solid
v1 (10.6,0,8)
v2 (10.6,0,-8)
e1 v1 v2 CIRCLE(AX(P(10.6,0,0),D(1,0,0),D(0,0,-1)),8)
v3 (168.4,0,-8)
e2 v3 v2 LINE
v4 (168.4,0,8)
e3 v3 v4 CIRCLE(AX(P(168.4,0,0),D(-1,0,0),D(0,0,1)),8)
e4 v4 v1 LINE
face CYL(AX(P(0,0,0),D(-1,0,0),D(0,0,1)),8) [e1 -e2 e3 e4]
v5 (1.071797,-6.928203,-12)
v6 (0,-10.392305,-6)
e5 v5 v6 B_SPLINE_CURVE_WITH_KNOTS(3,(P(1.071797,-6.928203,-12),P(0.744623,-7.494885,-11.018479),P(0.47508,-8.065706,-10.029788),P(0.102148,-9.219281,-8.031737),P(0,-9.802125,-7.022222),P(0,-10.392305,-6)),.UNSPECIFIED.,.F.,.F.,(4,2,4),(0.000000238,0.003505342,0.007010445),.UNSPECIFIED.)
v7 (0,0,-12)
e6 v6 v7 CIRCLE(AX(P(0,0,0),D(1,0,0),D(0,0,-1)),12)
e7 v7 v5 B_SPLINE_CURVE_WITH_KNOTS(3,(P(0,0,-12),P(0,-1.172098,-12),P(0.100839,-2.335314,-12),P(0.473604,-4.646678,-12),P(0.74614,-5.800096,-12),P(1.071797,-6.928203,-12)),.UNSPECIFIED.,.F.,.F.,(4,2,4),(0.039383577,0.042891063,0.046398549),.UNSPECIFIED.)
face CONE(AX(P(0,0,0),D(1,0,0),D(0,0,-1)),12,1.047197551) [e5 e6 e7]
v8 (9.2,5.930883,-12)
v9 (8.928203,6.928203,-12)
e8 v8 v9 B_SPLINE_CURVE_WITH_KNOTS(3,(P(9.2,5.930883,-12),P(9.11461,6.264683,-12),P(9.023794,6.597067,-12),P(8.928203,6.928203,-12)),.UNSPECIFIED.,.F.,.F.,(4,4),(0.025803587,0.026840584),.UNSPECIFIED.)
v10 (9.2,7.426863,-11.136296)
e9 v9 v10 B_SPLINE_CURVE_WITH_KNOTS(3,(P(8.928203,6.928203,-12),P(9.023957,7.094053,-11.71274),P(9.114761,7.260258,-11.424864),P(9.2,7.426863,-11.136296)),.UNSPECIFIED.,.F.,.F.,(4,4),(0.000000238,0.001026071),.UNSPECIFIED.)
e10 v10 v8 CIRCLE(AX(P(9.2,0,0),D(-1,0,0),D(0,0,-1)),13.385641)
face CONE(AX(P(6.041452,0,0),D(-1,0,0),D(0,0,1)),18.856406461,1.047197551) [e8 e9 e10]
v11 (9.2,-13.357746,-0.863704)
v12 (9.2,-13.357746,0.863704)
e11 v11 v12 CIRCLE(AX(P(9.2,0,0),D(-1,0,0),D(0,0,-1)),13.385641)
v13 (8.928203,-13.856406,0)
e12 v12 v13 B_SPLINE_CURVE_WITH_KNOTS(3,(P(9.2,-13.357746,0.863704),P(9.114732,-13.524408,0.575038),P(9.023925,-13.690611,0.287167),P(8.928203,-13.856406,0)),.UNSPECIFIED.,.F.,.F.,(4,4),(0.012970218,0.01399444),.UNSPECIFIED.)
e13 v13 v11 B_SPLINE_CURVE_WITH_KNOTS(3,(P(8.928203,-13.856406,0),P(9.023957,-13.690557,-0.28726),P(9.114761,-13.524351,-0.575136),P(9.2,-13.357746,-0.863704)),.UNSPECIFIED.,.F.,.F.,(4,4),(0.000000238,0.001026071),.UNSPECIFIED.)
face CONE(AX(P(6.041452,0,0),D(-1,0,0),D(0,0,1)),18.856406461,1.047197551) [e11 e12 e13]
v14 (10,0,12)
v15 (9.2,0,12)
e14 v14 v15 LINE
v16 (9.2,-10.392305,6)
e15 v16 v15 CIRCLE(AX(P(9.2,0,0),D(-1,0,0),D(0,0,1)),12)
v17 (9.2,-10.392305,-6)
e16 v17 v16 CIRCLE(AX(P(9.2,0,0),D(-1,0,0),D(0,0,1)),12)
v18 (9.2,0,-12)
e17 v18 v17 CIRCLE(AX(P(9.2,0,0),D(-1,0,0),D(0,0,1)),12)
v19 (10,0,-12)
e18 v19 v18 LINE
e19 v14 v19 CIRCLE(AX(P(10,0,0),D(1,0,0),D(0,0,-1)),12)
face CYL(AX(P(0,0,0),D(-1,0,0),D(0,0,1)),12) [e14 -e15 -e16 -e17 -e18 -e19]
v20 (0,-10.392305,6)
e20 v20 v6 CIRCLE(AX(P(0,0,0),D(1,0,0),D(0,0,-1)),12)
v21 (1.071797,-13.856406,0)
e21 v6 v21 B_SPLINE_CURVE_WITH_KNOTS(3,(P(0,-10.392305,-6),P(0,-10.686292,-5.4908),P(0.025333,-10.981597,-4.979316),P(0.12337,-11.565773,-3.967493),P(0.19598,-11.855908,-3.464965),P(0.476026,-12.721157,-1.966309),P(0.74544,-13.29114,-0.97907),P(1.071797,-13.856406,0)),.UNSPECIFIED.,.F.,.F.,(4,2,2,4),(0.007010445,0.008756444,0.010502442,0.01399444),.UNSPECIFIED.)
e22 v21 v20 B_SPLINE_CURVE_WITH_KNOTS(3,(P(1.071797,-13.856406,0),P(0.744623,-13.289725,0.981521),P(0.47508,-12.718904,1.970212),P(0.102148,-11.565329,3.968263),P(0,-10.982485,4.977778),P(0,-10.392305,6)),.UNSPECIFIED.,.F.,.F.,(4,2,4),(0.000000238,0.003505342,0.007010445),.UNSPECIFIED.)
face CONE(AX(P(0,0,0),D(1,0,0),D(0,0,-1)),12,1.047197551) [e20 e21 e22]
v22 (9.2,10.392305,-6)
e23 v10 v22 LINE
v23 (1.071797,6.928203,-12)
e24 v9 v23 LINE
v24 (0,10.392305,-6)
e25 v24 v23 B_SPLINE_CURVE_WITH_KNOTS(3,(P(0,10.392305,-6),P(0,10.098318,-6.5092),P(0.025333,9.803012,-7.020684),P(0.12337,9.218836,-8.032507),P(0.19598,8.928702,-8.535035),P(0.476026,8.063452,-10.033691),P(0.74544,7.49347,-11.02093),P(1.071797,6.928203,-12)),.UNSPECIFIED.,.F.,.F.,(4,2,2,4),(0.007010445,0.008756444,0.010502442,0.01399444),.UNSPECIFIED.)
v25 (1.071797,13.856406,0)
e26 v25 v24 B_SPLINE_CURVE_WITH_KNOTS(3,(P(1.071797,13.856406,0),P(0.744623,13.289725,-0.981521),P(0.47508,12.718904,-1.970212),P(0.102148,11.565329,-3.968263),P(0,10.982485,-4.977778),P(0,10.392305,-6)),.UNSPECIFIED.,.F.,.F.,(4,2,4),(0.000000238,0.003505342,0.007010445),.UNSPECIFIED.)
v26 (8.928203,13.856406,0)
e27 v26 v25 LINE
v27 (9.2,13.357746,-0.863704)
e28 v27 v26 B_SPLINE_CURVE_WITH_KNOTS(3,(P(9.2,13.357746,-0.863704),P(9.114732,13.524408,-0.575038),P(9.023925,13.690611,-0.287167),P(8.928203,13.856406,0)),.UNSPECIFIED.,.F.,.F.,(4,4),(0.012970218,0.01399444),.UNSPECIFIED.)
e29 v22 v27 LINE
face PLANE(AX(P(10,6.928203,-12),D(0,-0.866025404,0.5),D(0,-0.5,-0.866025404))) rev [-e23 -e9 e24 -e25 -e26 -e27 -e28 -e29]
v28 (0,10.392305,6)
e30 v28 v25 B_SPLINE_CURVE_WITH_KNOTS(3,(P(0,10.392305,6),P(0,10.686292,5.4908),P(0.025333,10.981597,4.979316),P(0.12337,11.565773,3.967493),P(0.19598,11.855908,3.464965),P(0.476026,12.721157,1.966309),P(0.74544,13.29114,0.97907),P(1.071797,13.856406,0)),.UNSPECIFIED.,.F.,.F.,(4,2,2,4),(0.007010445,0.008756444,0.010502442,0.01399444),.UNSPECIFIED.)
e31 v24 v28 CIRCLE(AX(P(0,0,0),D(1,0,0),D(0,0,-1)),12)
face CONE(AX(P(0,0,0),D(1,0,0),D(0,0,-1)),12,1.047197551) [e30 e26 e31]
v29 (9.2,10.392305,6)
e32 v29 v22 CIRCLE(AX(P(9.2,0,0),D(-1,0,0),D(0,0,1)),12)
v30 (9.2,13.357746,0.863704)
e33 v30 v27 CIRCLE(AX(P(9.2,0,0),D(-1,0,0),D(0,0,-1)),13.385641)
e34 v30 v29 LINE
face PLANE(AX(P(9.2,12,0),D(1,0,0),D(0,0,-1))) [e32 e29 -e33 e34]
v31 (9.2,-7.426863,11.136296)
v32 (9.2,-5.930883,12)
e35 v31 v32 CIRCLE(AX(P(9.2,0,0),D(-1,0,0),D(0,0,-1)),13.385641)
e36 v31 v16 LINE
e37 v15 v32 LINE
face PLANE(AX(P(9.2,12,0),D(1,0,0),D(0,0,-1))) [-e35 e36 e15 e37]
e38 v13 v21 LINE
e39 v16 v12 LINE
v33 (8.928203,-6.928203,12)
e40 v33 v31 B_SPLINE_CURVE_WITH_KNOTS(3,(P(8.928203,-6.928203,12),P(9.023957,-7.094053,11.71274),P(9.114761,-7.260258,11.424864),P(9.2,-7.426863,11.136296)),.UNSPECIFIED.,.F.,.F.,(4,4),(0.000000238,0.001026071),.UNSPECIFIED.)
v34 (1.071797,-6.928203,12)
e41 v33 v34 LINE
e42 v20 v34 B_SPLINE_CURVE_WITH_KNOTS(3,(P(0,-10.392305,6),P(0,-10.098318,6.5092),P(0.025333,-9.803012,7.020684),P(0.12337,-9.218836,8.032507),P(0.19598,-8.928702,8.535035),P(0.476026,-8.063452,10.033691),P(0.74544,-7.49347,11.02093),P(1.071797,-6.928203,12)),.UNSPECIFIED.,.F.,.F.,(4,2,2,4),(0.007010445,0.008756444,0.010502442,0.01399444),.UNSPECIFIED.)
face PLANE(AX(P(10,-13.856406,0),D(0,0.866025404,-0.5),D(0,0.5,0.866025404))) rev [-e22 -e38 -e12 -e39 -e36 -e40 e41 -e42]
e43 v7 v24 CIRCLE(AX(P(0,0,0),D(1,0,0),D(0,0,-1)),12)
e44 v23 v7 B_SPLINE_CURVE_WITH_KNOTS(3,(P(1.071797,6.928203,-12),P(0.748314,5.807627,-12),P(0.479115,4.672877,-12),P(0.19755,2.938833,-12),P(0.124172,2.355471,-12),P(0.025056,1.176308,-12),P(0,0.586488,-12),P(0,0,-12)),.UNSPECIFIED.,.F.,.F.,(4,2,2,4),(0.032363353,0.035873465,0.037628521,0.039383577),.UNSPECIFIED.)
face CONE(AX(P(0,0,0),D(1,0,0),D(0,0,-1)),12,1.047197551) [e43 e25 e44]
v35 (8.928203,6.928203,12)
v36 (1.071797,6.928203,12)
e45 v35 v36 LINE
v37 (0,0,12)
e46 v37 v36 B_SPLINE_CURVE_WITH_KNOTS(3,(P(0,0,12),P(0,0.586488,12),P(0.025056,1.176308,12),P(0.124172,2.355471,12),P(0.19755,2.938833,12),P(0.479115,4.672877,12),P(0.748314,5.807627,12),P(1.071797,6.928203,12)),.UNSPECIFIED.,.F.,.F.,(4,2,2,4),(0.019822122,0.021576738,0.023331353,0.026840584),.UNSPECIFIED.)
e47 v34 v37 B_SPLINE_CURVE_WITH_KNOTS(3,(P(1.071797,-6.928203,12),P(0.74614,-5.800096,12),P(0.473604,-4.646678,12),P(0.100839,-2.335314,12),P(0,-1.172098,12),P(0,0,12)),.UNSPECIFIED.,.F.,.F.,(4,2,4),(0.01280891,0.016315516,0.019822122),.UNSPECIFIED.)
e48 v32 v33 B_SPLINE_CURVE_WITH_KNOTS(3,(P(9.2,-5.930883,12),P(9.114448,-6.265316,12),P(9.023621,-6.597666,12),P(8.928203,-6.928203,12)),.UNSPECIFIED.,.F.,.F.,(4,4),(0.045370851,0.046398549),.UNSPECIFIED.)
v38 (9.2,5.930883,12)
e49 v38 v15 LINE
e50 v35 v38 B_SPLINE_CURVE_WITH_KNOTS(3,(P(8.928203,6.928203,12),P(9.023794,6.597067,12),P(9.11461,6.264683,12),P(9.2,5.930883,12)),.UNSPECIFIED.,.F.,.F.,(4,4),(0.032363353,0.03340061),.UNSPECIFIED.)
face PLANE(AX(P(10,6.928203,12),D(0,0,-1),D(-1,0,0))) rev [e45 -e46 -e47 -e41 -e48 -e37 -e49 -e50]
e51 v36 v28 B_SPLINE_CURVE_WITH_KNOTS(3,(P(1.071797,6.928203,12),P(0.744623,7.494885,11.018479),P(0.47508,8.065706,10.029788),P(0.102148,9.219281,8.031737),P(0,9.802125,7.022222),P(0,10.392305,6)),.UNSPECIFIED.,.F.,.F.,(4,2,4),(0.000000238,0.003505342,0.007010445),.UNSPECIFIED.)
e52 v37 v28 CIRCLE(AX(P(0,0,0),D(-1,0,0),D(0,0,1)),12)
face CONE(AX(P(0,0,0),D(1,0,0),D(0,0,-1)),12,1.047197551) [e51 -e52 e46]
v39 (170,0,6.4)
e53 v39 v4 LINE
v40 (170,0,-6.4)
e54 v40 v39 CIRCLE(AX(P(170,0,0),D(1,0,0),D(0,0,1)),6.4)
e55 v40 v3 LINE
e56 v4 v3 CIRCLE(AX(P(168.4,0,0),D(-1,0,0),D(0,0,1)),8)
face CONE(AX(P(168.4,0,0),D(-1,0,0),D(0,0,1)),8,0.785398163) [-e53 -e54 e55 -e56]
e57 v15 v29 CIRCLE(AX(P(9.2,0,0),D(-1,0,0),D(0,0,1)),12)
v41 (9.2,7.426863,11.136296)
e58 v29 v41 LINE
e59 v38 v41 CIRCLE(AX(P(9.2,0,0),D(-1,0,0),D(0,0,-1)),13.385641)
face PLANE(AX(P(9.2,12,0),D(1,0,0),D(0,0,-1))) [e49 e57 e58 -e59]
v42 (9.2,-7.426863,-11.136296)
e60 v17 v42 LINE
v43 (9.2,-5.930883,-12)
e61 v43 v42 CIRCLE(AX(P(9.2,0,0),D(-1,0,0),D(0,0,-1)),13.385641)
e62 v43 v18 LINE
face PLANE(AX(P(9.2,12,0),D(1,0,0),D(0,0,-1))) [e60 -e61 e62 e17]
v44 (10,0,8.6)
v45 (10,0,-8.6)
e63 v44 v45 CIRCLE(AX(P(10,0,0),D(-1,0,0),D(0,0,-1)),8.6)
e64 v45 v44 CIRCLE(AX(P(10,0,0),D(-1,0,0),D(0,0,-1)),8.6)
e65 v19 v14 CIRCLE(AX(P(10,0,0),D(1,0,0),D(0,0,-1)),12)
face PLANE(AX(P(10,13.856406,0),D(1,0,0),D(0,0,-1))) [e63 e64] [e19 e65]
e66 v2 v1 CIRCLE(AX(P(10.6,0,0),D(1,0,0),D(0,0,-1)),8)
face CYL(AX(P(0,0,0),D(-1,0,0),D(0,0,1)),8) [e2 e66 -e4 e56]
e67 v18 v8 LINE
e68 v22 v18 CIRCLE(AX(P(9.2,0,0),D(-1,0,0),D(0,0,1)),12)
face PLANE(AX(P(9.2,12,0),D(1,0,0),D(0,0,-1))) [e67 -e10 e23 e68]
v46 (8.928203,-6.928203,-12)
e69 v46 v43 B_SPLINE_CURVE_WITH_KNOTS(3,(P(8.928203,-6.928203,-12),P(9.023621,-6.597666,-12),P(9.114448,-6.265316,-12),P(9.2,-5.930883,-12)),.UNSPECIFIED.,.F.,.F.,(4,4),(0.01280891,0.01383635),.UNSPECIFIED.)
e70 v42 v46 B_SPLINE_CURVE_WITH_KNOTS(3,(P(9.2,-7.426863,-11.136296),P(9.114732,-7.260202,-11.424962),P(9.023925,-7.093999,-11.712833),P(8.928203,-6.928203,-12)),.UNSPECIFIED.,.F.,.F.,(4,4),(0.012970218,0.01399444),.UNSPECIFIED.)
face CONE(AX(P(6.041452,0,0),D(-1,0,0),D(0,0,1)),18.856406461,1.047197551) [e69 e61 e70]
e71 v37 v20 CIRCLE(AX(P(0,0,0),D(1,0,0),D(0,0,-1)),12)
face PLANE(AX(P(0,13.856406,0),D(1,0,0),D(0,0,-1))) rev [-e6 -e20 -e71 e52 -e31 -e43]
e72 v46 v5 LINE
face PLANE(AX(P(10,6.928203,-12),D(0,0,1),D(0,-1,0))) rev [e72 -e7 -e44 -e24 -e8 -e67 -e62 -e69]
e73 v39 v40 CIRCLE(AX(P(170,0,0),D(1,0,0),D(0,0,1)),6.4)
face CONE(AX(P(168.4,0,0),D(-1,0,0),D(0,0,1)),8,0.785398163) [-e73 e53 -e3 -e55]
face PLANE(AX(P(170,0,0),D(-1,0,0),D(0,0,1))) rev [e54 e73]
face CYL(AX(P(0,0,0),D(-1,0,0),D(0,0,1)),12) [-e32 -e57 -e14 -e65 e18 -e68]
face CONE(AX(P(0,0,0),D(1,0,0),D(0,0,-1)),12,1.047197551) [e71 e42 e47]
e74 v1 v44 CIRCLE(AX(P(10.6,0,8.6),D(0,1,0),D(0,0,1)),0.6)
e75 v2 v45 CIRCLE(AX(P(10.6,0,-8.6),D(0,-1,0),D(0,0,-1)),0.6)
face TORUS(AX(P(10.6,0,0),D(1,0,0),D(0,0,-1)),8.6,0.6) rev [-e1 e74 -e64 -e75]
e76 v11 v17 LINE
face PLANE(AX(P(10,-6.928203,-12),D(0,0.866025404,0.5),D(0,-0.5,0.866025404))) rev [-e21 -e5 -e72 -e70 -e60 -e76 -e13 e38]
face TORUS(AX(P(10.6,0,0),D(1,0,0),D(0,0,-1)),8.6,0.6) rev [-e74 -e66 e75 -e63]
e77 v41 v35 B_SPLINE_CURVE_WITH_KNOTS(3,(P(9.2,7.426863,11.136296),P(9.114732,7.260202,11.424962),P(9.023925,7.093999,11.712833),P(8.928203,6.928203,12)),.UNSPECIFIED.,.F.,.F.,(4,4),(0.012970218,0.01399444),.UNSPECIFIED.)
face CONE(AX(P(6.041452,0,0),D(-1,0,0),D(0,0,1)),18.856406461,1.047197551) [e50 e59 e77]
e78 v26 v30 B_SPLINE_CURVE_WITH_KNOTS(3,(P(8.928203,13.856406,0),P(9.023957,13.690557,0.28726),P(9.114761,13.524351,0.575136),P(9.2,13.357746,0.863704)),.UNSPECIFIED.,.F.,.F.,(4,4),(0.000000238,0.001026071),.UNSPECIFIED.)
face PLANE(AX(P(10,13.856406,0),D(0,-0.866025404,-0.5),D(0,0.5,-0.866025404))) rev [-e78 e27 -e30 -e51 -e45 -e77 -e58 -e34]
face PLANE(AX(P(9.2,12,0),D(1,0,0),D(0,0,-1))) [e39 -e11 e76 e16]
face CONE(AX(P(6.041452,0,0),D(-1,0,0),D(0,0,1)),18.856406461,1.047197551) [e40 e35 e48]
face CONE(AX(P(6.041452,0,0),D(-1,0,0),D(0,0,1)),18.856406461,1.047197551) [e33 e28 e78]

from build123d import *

# Parameters (mm, degrees)
BASE_EXTRUDE_DEPTH = 10
SKETCH4_W          = 0.8
SKETCH4_H          = 11.856406461
CHAMFER_2_SIZE     = 1.6
FILLET_2_R         = 0.6


with BuildPart() as part:
    # Sketch1 → Base-Extrude (new body)
    with BuildSketch(Plane(origin=(0, 0, 0), x_dir=(0, 0, -1), z_dir=(1, 0, 0))):
        Polygon((12, 6.92820323), (12, -6.92820323), (0, -13.856406461), (-12, -6.92820323), (-12, 6.92820323), (0, 13.856406461), align=None)
    extrude(amount=BASE_EXTRUDE_DEPTH)

    # Sketch2 → Boss-Revolve1 (revolve)
    with BuildSketch(Plane.XY, mode=Mode.PRIVATE) as boss_revolve1_sk:
        Polygon((0, 0), (170, 0), (170, 6.268), (170, 8), (0, 8), align=None)
    revolve(boss_revolve1_sk.sketch.rotate(Axis((0, 0, 0), (1, 0, 0)), 90), axis=Axis((0, 0, 0), (1, 0, 0)))

    # Sketch3 → Cut-Revolve1 (revolve, cut)
    with BuildSketch(Plane.XY):
        Polygon((0, 12), (3.958548116, 18.856406461), (3.958548116, 23.856406461), (-10, 23.856406461), (-10, 12), align=None)
    revolve(axis=Axis((0, 0, 0), (1, 0, 0)), mode=Mode.SUBTRACT)

    # Sketch5 → Cut-Revolve2 (revolve, cut)
    with BuildSketch(Plane.XY):
        Polygon((10, 12), (6.041451884, 18.856406461), (6.041451884, 23.856406461), (16.041451884, 23.856406461), (16.041451884, 12), align=None)
    revolve(axis=Axis((0, 0, 0), (1, 0, 0)), mode=Mode.SUBTRACT)

    # Sketch4 → Cut-Revolve3 (revolve, cut)
    with BuildSketch(Plane.XY, mode=Mode.PRIVATE) as cut_revolve3_sk:
        with Locations((9.6, 17.928203231)):
            Rectangle(SKETCH4_W, SKETCH4_H)
    revolve(cut_revolve3_sk.sketch.rotate(Axis((0, 0, 0), (1, 0, 0)), 270), axis=Axis((0, 0, 0), (1, 0, 0)), mode=Mode.SUBTRACT)

    # Chamfer 2
    chamfer_2_edges = [part.edges().sort_by_distance(p)[0] for p in [
        (170, 0, -8),
    ]]
    chamfer(chamfer_2_edges, length=CHAMFER_2_SIZE)

    # Fillet 2
    fillet_2_edges = [part.edges().sort_by_distance(p)[0] for p in [
        (10, 0, -8),
    ]]
    fillet(fillet_2_edges, radius=FILLET_2_R)


solid = part.part
